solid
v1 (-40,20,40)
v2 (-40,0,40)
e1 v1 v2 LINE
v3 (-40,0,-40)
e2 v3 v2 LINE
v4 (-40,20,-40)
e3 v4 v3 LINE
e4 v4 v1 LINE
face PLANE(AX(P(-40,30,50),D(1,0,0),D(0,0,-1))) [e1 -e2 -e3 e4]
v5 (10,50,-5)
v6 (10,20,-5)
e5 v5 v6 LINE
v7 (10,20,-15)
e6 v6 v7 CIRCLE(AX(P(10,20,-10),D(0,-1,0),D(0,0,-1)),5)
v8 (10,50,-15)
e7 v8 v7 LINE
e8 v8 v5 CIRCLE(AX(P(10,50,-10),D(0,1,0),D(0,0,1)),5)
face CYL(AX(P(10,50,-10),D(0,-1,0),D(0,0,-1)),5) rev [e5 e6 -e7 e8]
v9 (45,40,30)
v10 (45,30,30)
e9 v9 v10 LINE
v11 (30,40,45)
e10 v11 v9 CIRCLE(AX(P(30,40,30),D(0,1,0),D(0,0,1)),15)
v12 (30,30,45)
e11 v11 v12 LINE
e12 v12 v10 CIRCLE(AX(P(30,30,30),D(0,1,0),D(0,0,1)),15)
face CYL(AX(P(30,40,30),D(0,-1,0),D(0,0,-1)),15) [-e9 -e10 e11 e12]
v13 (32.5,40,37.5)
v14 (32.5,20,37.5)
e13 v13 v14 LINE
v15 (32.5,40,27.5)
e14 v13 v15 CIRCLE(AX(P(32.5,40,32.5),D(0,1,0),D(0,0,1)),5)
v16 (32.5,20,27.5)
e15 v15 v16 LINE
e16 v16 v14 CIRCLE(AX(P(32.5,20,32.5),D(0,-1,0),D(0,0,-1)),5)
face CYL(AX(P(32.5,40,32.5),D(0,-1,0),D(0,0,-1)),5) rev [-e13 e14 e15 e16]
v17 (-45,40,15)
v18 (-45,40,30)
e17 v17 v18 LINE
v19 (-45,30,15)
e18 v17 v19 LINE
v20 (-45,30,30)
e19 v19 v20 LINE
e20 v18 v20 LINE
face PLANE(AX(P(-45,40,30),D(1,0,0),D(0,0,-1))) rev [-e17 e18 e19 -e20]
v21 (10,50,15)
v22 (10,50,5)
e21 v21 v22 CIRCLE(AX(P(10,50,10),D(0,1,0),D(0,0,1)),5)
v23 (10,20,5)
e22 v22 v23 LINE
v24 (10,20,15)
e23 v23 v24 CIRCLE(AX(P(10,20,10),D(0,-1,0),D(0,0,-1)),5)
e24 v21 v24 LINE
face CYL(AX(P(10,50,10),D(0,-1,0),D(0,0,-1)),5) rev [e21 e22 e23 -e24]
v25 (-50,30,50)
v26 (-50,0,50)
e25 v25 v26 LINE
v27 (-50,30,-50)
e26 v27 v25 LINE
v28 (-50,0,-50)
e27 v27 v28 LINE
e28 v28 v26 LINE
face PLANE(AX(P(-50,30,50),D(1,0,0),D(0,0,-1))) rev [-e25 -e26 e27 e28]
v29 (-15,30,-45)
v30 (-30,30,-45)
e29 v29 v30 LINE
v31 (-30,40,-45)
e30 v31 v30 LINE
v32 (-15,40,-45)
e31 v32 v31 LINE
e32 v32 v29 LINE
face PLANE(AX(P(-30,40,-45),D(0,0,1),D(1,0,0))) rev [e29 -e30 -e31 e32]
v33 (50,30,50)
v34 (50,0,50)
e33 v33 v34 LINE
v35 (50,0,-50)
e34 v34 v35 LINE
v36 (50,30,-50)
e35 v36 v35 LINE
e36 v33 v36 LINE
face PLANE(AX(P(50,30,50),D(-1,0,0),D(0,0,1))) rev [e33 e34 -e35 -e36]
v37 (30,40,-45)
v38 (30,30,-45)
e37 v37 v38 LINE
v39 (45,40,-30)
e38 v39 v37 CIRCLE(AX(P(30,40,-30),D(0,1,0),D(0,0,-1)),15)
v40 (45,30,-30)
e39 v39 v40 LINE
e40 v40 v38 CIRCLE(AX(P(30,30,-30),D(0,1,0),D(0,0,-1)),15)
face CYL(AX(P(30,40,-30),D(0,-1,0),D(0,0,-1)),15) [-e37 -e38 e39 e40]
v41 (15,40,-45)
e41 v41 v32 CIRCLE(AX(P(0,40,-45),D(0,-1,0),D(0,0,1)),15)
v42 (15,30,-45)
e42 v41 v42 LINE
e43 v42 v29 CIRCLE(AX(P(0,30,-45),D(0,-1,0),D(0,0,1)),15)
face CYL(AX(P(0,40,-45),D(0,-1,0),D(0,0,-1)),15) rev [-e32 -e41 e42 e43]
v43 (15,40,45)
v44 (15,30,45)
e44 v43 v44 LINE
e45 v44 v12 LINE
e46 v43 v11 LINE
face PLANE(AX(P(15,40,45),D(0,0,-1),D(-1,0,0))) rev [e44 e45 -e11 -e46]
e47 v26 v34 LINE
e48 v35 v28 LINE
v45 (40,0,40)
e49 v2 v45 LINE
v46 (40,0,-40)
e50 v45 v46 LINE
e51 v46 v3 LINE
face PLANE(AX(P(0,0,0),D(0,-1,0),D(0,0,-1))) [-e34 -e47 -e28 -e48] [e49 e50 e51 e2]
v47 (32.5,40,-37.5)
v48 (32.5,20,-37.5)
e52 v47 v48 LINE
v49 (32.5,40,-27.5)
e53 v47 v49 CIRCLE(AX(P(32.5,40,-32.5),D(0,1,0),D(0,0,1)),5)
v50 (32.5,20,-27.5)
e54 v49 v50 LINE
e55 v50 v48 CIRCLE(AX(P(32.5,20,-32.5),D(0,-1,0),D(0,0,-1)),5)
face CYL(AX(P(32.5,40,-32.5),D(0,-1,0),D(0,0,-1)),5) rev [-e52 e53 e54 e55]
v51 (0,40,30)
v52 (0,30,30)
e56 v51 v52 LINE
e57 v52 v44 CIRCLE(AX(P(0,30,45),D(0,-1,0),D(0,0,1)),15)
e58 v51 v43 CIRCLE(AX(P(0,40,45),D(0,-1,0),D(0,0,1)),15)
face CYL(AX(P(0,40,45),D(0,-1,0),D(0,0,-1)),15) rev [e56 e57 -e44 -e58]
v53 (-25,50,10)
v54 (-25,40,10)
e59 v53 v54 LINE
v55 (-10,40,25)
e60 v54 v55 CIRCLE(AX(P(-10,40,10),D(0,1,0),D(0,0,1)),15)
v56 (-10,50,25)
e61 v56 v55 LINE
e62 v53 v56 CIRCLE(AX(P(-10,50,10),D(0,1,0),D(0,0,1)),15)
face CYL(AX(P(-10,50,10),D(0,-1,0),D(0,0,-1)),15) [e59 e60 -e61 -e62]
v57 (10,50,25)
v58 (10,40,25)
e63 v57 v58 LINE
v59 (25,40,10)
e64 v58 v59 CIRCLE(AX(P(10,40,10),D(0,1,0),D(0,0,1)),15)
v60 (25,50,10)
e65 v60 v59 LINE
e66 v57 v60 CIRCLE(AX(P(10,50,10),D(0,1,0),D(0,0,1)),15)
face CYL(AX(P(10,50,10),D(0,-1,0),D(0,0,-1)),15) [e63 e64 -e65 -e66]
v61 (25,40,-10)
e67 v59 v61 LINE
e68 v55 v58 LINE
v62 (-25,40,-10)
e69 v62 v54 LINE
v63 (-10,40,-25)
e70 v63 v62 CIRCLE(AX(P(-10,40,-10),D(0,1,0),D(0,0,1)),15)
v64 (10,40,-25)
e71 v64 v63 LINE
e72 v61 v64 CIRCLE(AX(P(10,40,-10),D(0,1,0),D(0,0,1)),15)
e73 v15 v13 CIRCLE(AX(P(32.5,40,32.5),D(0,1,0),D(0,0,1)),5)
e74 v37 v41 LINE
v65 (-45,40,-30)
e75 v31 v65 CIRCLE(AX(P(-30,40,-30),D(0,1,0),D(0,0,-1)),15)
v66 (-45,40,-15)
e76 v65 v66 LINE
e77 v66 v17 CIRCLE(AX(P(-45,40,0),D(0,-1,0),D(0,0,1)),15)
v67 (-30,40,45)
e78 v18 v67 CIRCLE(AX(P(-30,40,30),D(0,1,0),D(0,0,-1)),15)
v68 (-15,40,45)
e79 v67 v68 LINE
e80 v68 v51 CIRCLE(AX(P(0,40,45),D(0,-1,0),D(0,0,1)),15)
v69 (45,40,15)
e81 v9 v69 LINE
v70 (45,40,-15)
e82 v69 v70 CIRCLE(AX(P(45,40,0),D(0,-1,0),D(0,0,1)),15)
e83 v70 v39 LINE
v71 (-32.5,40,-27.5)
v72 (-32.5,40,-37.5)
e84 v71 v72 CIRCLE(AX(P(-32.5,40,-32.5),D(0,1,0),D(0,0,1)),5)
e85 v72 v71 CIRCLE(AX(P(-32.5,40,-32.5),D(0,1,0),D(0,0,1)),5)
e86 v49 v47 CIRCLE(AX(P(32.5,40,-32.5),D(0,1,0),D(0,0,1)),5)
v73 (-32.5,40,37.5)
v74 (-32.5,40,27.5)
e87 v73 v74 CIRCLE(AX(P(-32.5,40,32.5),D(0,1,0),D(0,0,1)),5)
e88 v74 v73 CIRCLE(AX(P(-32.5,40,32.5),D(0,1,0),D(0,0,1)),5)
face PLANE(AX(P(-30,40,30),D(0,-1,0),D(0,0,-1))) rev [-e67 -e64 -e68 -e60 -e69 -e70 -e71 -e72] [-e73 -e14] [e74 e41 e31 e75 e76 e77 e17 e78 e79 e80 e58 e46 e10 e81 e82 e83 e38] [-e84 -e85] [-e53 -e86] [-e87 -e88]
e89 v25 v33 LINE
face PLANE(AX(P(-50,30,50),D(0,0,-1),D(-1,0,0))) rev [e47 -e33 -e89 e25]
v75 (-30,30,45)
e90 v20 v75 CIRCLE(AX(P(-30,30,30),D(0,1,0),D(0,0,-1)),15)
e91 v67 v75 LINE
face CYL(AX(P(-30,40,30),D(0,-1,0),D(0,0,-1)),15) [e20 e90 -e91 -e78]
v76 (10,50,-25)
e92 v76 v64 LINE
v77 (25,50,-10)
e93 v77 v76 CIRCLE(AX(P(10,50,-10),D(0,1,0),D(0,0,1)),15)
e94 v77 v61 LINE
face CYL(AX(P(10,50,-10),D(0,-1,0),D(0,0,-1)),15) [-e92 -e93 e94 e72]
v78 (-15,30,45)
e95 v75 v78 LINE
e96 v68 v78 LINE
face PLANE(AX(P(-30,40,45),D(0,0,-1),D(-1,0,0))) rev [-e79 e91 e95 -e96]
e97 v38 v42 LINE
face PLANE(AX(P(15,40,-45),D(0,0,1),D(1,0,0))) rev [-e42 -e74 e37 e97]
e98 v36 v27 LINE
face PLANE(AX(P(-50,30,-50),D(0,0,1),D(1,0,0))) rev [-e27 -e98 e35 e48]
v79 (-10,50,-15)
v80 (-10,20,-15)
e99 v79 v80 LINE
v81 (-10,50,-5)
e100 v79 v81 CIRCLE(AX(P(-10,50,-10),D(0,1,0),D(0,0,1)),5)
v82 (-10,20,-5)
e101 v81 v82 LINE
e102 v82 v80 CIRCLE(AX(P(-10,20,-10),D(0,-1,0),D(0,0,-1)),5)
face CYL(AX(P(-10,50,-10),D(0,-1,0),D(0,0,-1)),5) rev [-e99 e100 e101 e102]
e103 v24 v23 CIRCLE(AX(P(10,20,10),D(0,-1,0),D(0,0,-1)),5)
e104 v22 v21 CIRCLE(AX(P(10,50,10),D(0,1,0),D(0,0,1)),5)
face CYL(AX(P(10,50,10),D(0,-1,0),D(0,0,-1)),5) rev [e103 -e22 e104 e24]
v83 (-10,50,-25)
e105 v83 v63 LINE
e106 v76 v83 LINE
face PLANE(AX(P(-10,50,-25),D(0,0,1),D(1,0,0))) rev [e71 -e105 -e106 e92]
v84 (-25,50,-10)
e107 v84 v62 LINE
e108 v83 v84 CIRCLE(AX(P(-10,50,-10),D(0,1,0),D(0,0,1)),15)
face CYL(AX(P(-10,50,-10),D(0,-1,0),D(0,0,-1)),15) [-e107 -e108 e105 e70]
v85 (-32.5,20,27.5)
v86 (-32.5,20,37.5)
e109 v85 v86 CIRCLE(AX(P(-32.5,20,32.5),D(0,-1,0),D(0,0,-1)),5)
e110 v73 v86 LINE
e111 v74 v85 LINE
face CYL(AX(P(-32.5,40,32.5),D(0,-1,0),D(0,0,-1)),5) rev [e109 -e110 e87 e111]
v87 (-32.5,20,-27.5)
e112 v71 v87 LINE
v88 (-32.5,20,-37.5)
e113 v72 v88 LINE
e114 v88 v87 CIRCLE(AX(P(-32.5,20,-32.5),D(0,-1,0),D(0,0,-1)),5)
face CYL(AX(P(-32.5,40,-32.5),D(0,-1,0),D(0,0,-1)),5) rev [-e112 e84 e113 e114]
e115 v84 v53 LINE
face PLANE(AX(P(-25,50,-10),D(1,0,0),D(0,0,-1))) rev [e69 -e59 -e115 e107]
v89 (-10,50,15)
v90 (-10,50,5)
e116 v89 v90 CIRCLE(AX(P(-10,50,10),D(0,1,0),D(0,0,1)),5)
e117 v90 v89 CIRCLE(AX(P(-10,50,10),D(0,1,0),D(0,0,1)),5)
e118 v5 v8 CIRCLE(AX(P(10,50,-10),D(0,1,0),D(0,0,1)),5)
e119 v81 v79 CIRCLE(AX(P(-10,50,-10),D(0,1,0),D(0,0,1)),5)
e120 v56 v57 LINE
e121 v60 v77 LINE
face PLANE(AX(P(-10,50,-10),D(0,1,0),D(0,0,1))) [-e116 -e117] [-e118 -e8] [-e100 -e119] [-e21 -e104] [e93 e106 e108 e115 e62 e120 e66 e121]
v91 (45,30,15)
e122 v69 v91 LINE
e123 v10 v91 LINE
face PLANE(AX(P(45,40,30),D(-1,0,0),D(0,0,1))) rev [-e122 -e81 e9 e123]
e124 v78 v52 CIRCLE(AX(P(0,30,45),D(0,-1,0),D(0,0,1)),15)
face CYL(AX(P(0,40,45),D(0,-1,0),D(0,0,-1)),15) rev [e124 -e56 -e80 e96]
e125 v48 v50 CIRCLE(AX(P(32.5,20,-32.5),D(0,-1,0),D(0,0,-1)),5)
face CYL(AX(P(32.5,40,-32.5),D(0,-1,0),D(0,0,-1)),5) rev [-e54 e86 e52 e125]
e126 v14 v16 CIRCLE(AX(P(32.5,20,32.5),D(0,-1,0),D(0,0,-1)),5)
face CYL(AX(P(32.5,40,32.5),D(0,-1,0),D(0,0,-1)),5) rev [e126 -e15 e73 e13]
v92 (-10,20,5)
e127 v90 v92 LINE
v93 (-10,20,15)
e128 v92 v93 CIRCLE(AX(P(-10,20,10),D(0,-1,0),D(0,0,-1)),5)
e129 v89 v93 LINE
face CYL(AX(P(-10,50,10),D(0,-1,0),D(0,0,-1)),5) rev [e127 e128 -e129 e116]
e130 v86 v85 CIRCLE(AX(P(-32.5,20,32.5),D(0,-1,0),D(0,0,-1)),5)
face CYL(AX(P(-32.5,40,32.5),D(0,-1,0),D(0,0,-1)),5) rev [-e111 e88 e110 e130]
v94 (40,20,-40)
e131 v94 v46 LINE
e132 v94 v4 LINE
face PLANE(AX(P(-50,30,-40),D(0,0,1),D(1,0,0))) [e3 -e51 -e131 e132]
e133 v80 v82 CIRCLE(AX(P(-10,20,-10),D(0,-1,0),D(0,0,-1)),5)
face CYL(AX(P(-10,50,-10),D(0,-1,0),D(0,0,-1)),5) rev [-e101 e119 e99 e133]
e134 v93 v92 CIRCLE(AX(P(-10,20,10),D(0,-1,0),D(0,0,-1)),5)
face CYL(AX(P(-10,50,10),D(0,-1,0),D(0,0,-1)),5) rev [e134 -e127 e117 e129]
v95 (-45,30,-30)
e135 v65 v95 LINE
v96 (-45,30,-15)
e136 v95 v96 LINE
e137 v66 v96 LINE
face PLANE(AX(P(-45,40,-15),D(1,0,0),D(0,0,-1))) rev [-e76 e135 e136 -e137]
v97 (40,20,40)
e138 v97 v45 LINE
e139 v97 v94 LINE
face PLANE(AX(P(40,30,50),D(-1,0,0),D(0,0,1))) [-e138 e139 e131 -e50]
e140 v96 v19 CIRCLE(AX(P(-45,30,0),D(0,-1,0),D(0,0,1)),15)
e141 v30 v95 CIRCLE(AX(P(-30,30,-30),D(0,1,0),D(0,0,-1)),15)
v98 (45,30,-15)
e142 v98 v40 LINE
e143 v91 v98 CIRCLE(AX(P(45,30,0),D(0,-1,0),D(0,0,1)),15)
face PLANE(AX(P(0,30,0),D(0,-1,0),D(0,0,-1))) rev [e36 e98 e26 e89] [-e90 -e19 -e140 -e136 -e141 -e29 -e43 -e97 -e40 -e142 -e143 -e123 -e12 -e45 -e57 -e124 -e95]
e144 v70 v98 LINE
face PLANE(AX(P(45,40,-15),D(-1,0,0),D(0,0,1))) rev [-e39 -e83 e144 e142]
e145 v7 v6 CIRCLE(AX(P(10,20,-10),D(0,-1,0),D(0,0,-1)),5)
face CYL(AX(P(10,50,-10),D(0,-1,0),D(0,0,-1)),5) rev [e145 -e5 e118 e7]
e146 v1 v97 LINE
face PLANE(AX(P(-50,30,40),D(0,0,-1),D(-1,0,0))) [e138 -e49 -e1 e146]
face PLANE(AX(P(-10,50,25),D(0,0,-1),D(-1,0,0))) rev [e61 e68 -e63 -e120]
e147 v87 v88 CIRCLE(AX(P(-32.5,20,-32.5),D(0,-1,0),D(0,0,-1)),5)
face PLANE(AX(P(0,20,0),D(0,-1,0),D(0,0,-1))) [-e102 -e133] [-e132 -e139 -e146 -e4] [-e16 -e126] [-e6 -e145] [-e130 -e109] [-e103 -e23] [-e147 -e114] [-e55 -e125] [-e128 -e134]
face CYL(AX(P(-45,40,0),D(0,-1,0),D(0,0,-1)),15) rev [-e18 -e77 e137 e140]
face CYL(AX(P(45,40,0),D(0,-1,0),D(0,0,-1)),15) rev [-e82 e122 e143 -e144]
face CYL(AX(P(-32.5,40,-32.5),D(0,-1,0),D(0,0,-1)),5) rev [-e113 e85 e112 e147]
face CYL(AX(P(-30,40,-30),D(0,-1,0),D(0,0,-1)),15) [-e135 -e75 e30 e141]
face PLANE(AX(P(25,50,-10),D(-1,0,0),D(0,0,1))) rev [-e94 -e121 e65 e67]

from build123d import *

# Parameters (mm, degrees)
BASE_SQUARE_SKETCH_W        = 100
BASE_SQUARE_SKETCH_H        = 100
BASE_BLOCK_100X100X30_DEPTH = 30
BASE_SHELL_10MM_T           = -10
CROSS_PLATE_SKETCH_R        = 5
CROSS_PLATE_10MM_DEPTH      = 10
PLATE_HOLES_SKETCH_R        = 5
PLATE_ARM_HOLES_4X_DEPTH    = 82.240384046
CENTRE_BOSS_SKETCH_R        = 5
CENTRE_BOSS_10MM_DEPTH      = 10
CENTRE_HOLES_SKETCH_R       = 5
CENTRE_BOSS_HOLES_4X_DEPTH  = 87.602540378


with BuildPart() as part:
    # Base Square Sketch → Base Block 100x100x30 (new body)
    with BuildSketch(Plane(origin=(0, 0, 0), x_dir=(1, 0, 0), z_dir=(0, 1, 0))):
        Rectangle(BASE_SQUARE_SKETCH_W, BASE_SQUARE_SKETCH_H)
    extrude(amount=BASE_BLOCK_100X100X30_DEPTH)

    # Base Shell 10mm
    base_shell_10mm_openings = [part.faces().sort_by_distance(p)[0] for p in [
        (0, 0, 0),
    ]]
    offset(amount=BASE_SHELL_10MM_T, openings=base_shell_10mm_openings, kind=Kind.INTERSECTION)

    # Cross Plate Sketch → Cross Plate 10mm (add)
    with BuildSketch(Plane(origin=(0, 30, 0), x_dir=(1, 0, 0), z_dir=(0, 1, 0))):
        with BuildLine():
            Line((15, 45), (30, 45))
            ThreePointArc((30, 45), (40.606601718, 40.606601718), (45, 30))
            Line((45, 30), (45, 15))
            ThreePointArc((45, 15), (30, 0), (45, -15))
            Line((45, -15), (45, -30))
            ThreePointArc((45, -30), (40.606601718, -40.606601718), (30, -45))
            Line((30, -45), (15, -45))
            ThreePointArc((15, -45), (0, -30), (-15, -45))
            Line((-15, -45), (-30, -45))
            ThreePointArc((-30, -45), (-40.606601718, -40.606601718), (-45, -30))
            Line((-45, -30), (-45, -15))
            ThreePointArc((-45, -15), (-30, 0), (-45, 15))
            Line((-45, 15), (-45, 30))
            ThreePointArc((-45, 30), (-40.606601718, 40.606601718), (-30, 45))
            Line((-30, 45), (-15, 45))
            ThreePointArc((-15, 45), (0, 30), (15, 45))
        make_face()
        with Locations(Location((-32.5, 32.5, 0), (0, 0, 270))):
            Circle(CROSS_PLATE_SKETCH_R, mode=Mode.SUBTRACT)
        with Locations(Location((32.5, 32.5, 0), (0, 0, 270))):
            Circle(CROSS_PLATE_SKETCH_R, mode=Mode.SUBTRACT)
        with Locations(Location((-32.5, -32.5, 0), (0, 0, 270))):
            Circle(CROSS_PLATE_SKETCH_R, mode=Mode.SUBTRACT)
        with Locations(Location((32.5, -32.5, 0), (0, 0, 270))):
            Circle(CROSS_PLATE_SKETCH_R, mode=Mode.SUBTRACT)
    extrude(amount=CROSS_PLATE_10MM_DEPTH)

    # Plate Holes Sketch → Plate Arm Holes 4x (cut, through all)
    with BuildSketch(Plane(origin=(0, 40, 0), x_dir=(1, 0, 0), z_dir=(0, 1, 0))):
        with Locations(Location((-32.5, 32.5, 0), (0, 0, 90))):
            Circle(PLATE_HOLES_SKETCH_R)
        with Locations(Location((32.5, 32.5, 0), (0, 0, 90))):
            Circle(PLATE_HOLES_SKETCH_R)
        with Locations(Location((32.5, -32.5, 0), (0, 0, 90))):
            Circle(PLATE_HOLES_SKETCH_R)
        with Locations(Location((-32.5, -32.5, 0), (0, 0, 90))):
            Circle(PLATE_HOLES_SKETCH_R)
    extrude(amount=-PLATE_ARM_HOLES_4X_DEPTH, mode=Mode.SUBTRACT)

    # Centre Boss Sketch → Centre Boss 10mm (add)
    with BuildSketch(Plane(origin=(0, 40, 0), x_dir=(1, 0, 0), z_dir=(0, 1, 0))):
        with BuildLine():
            Line((-25, 10), (-25, -10))
            ThreePointArc((-25, -10), (-20.606601718, -20.606601718), (-10, -25))
            Line((-10, -25), (10, -25))
            ThreePointArc((10, -25), (20.606601718, -20.606601718), (25, -10))
            Line((25, -10), (25, 10))
            ThreePointArc((25, 10), (20.606601718, 20.606601718), (10, 25))
            Line((10, 25), (-10, 25))
            ThreePointArc((-10, 25), (-20.606601718, 20.606601718), (-25, 10))
        make_face()
        with Locations(Location((-10, 10, 0), (0, 0, 270))):
            Circle(CENTRE_BOSS_SKETCH_R, mode=Mode.SUBTRACT)
        with Locations(Location((10, 10, 0), (0, 0, 270))):
            Circle(CENTRE_BOSS_SKETCH_R, mode=Mode.SUBTRACT)
        with Locations(Location((10, -10, 0), (0, 0, 270))):
            Circle(CENTRE_BOSS_SKETCH_R, mode=Mode.SUBTRACT)
        with Locations(Location((-10, -10, 0), (0, 0, 270))):
            Circle(CENTRE_BOSS_SKETCH_R, mode=Mode.SUBTRACT)
    extrude(amount=CENTRE_BOSS_10MM_DEPTH)

    # Centre Holes Sketch → Centre Boss Holes 4x (cut, through all)
    with BuildSketch(Plane(origin=(0, 50, 0), x_dir=(1, 0, 0), z_dir=(0, 1, 0))):
        with Locations(Location((-10, 10, 0), (0, 0, 90))):
            Circle(CENTRE_HOLES_SKETCH_R)
        with Locations(Location((10, 10, 0), (0, 0, 90))):
            Circle(CENTRE_HOLES_SKETCH_R)
        with Locations(Location((10, -10, 0), (0, 0, 90))):
            Circle(CENTRE_HOLES_SKETCH_R)
        with Locations(Location((-10, -10, 0), (0, 0, 90))):
            Circle(CENTRE_HOLES_SKETCH_R)
    extrude(amount=-CENTRE_BOSS_HOLES_4X_DEPTH, mode=Mode.SUBTRACT)


solid = part.part
